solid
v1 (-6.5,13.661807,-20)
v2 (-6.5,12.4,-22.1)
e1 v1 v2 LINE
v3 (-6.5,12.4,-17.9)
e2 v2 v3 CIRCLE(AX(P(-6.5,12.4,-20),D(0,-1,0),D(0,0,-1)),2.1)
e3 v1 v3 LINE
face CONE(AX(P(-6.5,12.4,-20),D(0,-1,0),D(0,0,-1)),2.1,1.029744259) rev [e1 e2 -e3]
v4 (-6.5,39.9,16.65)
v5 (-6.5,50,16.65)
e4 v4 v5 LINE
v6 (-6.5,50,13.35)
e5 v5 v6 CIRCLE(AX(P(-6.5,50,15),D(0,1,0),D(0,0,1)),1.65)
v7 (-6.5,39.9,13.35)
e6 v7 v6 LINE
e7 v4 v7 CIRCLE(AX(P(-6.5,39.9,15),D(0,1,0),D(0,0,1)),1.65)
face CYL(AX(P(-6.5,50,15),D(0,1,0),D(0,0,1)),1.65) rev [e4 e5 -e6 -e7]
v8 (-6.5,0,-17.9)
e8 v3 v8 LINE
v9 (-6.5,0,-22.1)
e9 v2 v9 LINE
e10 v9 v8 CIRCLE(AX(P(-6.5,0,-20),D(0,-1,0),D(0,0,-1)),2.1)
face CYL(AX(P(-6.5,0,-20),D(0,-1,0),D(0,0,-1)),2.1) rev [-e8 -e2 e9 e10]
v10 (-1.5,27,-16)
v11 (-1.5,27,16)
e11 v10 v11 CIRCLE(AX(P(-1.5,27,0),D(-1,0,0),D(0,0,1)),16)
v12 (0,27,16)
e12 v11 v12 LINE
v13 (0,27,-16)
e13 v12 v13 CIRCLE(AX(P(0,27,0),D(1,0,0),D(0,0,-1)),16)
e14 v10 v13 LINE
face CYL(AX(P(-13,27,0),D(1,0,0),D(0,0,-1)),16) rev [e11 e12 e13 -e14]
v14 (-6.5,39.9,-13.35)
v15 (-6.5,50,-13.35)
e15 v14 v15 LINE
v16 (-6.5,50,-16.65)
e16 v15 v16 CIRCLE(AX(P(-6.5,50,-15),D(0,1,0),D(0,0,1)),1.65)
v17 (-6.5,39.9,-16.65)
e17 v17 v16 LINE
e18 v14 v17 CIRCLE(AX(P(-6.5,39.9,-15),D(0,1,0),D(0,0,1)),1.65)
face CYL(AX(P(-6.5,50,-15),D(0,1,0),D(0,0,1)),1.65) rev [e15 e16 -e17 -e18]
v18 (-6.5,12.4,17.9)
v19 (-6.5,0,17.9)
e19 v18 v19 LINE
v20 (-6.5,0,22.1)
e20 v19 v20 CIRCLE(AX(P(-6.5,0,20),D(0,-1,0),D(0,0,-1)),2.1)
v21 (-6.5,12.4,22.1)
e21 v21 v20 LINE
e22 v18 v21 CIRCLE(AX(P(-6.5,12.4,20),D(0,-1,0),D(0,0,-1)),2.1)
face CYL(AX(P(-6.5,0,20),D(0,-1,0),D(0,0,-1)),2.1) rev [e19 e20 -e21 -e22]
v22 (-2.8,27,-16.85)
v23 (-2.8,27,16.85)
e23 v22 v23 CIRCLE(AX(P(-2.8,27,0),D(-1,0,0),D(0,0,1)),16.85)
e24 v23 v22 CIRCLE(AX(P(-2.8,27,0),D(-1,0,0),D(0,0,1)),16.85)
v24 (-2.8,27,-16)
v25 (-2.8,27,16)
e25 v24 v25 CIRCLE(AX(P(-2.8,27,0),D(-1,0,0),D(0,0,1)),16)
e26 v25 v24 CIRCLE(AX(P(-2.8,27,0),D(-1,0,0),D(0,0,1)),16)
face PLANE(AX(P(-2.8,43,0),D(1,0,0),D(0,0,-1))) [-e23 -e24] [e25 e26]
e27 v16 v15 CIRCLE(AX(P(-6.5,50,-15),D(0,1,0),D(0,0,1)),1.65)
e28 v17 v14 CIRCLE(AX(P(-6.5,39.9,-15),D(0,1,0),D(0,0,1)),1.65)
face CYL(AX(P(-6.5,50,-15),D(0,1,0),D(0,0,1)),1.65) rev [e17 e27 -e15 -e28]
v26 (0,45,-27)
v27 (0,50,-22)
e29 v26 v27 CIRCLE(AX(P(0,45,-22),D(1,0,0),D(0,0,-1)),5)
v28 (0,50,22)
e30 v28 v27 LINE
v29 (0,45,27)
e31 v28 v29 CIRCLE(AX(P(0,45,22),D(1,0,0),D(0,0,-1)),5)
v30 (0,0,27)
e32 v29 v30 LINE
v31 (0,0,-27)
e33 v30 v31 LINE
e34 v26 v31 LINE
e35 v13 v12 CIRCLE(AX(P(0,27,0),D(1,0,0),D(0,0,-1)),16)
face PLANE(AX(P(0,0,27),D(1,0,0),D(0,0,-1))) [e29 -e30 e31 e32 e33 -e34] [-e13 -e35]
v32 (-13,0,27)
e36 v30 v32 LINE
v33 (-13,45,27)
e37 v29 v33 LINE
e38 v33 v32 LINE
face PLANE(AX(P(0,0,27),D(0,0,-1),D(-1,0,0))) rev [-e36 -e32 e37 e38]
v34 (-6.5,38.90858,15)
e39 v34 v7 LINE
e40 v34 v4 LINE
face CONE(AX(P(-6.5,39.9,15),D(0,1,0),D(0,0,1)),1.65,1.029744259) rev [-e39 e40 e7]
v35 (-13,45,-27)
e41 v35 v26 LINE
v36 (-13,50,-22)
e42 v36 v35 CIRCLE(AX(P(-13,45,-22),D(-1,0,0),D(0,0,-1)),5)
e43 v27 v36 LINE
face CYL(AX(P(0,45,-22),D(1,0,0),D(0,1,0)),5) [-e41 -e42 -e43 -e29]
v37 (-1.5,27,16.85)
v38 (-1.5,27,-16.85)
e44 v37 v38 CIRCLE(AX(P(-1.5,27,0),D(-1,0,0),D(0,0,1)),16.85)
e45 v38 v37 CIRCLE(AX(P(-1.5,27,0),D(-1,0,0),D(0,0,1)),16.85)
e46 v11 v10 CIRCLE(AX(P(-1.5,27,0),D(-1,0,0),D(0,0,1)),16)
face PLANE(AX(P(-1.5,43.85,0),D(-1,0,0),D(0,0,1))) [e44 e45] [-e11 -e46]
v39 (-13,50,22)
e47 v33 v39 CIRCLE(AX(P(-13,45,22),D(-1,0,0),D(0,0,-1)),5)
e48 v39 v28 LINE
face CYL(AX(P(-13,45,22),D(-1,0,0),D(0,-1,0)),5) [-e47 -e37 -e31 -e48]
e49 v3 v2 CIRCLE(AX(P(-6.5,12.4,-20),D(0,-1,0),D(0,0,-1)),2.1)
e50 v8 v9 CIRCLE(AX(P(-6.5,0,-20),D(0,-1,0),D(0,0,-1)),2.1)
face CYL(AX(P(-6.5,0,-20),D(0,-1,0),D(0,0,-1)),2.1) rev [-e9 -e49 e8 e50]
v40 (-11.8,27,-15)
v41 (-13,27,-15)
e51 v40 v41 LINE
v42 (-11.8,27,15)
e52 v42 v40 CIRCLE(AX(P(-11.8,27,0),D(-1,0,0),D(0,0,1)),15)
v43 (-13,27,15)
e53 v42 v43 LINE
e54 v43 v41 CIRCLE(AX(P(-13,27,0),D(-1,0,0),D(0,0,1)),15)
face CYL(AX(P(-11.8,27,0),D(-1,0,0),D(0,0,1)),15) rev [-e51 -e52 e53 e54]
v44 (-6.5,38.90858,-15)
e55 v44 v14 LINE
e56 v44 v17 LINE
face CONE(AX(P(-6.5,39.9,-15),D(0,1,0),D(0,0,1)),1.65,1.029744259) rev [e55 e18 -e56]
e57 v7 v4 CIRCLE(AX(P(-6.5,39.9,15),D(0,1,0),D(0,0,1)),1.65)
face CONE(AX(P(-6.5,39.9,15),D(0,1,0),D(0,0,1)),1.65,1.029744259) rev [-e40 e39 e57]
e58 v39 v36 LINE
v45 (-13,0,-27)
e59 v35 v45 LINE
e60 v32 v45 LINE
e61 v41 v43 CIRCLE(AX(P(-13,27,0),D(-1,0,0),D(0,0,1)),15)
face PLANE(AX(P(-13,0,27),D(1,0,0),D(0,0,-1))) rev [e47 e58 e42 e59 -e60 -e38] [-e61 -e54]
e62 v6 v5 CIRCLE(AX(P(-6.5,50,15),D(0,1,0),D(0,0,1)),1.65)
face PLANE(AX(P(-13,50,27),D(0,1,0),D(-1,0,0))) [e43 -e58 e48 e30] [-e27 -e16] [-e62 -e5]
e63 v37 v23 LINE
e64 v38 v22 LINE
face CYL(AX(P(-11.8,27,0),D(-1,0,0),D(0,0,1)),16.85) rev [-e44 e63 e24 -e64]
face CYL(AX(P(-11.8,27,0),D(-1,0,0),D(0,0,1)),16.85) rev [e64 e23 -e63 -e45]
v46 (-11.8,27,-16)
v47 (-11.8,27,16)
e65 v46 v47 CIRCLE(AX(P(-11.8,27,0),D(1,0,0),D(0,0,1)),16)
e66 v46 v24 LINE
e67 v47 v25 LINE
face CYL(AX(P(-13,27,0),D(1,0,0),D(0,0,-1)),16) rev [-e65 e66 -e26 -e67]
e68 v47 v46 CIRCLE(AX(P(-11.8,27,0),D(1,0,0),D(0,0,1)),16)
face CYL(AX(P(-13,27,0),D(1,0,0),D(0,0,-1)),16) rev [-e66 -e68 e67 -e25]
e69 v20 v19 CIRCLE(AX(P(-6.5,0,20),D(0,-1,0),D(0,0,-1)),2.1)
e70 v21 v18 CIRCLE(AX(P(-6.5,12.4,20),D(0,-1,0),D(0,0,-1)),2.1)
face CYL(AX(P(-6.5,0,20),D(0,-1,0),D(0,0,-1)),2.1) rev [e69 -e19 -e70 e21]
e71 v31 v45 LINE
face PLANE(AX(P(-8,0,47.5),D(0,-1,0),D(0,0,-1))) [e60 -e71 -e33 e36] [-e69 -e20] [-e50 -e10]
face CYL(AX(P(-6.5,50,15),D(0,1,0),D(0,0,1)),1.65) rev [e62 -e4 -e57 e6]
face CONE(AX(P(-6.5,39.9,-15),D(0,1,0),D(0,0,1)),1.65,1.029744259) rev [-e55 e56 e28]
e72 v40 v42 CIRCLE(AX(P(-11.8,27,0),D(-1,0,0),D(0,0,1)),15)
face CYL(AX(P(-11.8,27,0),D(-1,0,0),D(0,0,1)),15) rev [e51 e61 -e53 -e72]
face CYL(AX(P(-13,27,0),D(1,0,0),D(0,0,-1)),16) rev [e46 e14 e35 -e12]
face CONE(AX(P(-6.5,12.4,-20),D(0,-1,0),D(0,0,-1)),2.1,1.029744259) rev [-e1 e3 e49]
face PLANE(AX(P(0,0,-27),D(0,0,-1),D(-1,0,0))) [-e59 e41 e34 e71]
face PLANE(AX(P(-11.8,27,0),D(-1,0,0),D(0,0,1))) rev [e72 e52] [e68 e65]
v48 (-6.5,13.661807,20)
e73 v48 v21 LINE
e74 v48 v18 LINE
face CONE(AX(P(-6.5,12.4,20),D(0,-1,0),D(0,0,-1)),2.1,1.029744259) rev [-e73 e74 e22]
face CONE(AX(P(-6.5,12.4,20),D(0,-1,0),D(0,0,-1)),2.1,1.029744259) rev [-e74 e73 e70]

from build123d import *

# Parameters (mm, degrees)
EXTRUDE_1_DEPTH        = 27
SKETCH_2_R             = 16
CUT_EXTRUDE_1_DEPTH    = 107.437775249
EXTRUDE_START          = -1.2
SKETCH_3_R             = 16
SKETCH_3_R_2           = 15
EXTRUDE_1_2_DEPTH      = 1.2
SKETCH_4_W             = 1.3
SKETCH_4_H             = 0.85
SKETCH_5_W             = 103
SKETCH_5_H             = 105
EXTRUDE_2_DEPTH        = 13
FILLET_1_R             = 5
CUT_EXTRUDE_2_DEPTH    = 13
HOLE_WIZARD_M5_1_D     = 4.2
HOLE_WIZARD_M5_1_DEPTH = 12.4
HOLE_WIZARD_M5_1_TIP   = 1.2618073
HOLE_WIZARD_M4_1_D     = 3.3
HOLE_WIZARD_M4_1_DEPTH = 10.1
HOLE_WIZARD_M4_1_TIP   = 0.991420021


with BuildPart() as part:
    # 草图1 → Extrude 1 (new, symmetric)
    with BuildSketch(Plane.XY):
        Polygon((90, 0), (0, 0), (0, 50), (-13, 50), (-13, -13), (90, -13), align=None)
    extrude(amount=EXTRUDE_1_DEPTH, both=True)

    # 草图2 → 切除-拉伸1 (cut, through all)
    with BuildSketch(Plane(origin=(0, 0, 0), x_dir=(0, 0, -1), z_dir=(1, 0, 0))):
        with Locations((0, 27)):
            Circle(SKETCH_2_R)
    extrude(amount=-CUT_EXTRUDE_1_DEPTH, mode=Mode.SUBTRACT)

    # 草图3 → Extrude 1 2 (add)
    with BuildSketch(Plane.ZY.offset(13).offset(EXTRUDE_START)):
        with Locations(Location((0, 27, 0), (0, 0, 180))):
            Circle(SKETCH_3_R)
        with Locations((0, 27)):
            Circle(SKETCH_3_R_2, mode=Mode.SUBTRACT)
    extrude(amount=EXTRUDE_1_2_DEPTH)

    # 草图4 → 切除-旋转1 (revolve, cut)
    with BuildSketch(Plane.XY, mode=Mode.PRIVATE) as cut_revolve_1_sk:
        with Locations((-2.15, 43.425)):
            Rectangle(SKETCH_4_W, SKETCH_4_H)
    revolve(cut_revolve_1_sk.sketch.rotate(Axis((-11.8, 27, 0), (1, 0, 0)), 90), axis=Axis((-11.8, 27, 0), (1, 0, 0)), mode=Mode.SUBTRACT)

    # 草图5 → 凸台-拉伸2 (add)
    with BuildSketch(Plane(origin=(0, 0, 0), x_dir=(1, 0, 0), z_dir=(0, 1, 0))):
        with Locations((38.5, 0)):
            Rectangle(SKETCH_5_W, SKETCH_5_H)
    extrude(amount=-EXTRUDE_2_DEPTH)

    # 圆角1
    fillet_1_edges = [part.edges().sort_by_distance(p)[0] for p in [
        (-6.5, 50, 27),
        (-13, -6.5, 52.5),
        (90, -6.5, -52.5),
        (90, -6.5, 52.5),
        (-13, -6.5, -52.5),
        (-6.5, 50, -27),
    ]]
    fillet(fillet_1_edges, radius=FILLET_1_R)

    # 草图6 → 切除-拉伸2 (cut)
    with BuildSketch(Plane.XZ.offset(13)):
        with BuildLine():
            Line((-13, 47.5), (-13, -47.5))
            ThreePointArc((-13, -47.5), (-11.535533906, -51.035533906), (-8, -52.5))
            Line((-8, -52.5), (85, -52.5))
            ThreePointArc((85, -52.5), (88.535533906, -51.035533906), (90, -47.5))
            Line((90, -47.5), (90, 47.5))
            ThreePointArc((90, 47.5), (88.535533906, 51.035533906), (85, 52.5))
            Line((85, 52.5), (-8, 52.5))
            ThreePointArc((-8, 52.5), (-11.535533906, 51.035533906), (-13, 47.5))
        make_face()
    extrude(amount=-CUT_EXTRUDE_2_DEPTH, mode=Mode.SUBTRACT)

    # M5 螺纹孔1
    with Locations(Plane(origin=(-6.5, 0, 20), x_dir=(0, 0, -1), z_dir=(0, -1, 0))):
        with Locations((0, 0), (40, 0)):
            Hole(HOLE_WIZARD_M5_1_D / 2, depth=HOLE_WIZARD_M5_1_DEPTH)
            with Locations((0, 0, -(HOLE_WIZARD_M5_1_DEPTH + HOLE_WIZARD_M5_1_TIP / 2))):  # 118° drill point
                Cone(0, HOLE_WIZARD_M5_1_D / 2, HOLE_WIZARD_M5_1_TIP, mode=Mode.SUBTRACT)

    # M4 螺纹孔1
    with Locations(Plane(origin=(-6.5, 50, -15), x_dir=(1, 0, 0), z_dir=(0, 1, 0))):
        with Locations((0, 0), (0, -30)):
            Hole(HOLE_WIZARD_M4_1_D / 2, depth=HOLE_WIZARD_M4_1_DEPTH)
            with Locations((0, 0, -(HOLE_WIZARD_M4_1_DEPTH + HOLE_WIZARD_M4_1_TIP / 2))):  # 118° drill point
                Cone(0, HOLE_WIZARD_M4_1_D / 2, HOLE_WIZARD_M4_1_TIP, mode=Mode.SUBTRACT)


solid = part.part
